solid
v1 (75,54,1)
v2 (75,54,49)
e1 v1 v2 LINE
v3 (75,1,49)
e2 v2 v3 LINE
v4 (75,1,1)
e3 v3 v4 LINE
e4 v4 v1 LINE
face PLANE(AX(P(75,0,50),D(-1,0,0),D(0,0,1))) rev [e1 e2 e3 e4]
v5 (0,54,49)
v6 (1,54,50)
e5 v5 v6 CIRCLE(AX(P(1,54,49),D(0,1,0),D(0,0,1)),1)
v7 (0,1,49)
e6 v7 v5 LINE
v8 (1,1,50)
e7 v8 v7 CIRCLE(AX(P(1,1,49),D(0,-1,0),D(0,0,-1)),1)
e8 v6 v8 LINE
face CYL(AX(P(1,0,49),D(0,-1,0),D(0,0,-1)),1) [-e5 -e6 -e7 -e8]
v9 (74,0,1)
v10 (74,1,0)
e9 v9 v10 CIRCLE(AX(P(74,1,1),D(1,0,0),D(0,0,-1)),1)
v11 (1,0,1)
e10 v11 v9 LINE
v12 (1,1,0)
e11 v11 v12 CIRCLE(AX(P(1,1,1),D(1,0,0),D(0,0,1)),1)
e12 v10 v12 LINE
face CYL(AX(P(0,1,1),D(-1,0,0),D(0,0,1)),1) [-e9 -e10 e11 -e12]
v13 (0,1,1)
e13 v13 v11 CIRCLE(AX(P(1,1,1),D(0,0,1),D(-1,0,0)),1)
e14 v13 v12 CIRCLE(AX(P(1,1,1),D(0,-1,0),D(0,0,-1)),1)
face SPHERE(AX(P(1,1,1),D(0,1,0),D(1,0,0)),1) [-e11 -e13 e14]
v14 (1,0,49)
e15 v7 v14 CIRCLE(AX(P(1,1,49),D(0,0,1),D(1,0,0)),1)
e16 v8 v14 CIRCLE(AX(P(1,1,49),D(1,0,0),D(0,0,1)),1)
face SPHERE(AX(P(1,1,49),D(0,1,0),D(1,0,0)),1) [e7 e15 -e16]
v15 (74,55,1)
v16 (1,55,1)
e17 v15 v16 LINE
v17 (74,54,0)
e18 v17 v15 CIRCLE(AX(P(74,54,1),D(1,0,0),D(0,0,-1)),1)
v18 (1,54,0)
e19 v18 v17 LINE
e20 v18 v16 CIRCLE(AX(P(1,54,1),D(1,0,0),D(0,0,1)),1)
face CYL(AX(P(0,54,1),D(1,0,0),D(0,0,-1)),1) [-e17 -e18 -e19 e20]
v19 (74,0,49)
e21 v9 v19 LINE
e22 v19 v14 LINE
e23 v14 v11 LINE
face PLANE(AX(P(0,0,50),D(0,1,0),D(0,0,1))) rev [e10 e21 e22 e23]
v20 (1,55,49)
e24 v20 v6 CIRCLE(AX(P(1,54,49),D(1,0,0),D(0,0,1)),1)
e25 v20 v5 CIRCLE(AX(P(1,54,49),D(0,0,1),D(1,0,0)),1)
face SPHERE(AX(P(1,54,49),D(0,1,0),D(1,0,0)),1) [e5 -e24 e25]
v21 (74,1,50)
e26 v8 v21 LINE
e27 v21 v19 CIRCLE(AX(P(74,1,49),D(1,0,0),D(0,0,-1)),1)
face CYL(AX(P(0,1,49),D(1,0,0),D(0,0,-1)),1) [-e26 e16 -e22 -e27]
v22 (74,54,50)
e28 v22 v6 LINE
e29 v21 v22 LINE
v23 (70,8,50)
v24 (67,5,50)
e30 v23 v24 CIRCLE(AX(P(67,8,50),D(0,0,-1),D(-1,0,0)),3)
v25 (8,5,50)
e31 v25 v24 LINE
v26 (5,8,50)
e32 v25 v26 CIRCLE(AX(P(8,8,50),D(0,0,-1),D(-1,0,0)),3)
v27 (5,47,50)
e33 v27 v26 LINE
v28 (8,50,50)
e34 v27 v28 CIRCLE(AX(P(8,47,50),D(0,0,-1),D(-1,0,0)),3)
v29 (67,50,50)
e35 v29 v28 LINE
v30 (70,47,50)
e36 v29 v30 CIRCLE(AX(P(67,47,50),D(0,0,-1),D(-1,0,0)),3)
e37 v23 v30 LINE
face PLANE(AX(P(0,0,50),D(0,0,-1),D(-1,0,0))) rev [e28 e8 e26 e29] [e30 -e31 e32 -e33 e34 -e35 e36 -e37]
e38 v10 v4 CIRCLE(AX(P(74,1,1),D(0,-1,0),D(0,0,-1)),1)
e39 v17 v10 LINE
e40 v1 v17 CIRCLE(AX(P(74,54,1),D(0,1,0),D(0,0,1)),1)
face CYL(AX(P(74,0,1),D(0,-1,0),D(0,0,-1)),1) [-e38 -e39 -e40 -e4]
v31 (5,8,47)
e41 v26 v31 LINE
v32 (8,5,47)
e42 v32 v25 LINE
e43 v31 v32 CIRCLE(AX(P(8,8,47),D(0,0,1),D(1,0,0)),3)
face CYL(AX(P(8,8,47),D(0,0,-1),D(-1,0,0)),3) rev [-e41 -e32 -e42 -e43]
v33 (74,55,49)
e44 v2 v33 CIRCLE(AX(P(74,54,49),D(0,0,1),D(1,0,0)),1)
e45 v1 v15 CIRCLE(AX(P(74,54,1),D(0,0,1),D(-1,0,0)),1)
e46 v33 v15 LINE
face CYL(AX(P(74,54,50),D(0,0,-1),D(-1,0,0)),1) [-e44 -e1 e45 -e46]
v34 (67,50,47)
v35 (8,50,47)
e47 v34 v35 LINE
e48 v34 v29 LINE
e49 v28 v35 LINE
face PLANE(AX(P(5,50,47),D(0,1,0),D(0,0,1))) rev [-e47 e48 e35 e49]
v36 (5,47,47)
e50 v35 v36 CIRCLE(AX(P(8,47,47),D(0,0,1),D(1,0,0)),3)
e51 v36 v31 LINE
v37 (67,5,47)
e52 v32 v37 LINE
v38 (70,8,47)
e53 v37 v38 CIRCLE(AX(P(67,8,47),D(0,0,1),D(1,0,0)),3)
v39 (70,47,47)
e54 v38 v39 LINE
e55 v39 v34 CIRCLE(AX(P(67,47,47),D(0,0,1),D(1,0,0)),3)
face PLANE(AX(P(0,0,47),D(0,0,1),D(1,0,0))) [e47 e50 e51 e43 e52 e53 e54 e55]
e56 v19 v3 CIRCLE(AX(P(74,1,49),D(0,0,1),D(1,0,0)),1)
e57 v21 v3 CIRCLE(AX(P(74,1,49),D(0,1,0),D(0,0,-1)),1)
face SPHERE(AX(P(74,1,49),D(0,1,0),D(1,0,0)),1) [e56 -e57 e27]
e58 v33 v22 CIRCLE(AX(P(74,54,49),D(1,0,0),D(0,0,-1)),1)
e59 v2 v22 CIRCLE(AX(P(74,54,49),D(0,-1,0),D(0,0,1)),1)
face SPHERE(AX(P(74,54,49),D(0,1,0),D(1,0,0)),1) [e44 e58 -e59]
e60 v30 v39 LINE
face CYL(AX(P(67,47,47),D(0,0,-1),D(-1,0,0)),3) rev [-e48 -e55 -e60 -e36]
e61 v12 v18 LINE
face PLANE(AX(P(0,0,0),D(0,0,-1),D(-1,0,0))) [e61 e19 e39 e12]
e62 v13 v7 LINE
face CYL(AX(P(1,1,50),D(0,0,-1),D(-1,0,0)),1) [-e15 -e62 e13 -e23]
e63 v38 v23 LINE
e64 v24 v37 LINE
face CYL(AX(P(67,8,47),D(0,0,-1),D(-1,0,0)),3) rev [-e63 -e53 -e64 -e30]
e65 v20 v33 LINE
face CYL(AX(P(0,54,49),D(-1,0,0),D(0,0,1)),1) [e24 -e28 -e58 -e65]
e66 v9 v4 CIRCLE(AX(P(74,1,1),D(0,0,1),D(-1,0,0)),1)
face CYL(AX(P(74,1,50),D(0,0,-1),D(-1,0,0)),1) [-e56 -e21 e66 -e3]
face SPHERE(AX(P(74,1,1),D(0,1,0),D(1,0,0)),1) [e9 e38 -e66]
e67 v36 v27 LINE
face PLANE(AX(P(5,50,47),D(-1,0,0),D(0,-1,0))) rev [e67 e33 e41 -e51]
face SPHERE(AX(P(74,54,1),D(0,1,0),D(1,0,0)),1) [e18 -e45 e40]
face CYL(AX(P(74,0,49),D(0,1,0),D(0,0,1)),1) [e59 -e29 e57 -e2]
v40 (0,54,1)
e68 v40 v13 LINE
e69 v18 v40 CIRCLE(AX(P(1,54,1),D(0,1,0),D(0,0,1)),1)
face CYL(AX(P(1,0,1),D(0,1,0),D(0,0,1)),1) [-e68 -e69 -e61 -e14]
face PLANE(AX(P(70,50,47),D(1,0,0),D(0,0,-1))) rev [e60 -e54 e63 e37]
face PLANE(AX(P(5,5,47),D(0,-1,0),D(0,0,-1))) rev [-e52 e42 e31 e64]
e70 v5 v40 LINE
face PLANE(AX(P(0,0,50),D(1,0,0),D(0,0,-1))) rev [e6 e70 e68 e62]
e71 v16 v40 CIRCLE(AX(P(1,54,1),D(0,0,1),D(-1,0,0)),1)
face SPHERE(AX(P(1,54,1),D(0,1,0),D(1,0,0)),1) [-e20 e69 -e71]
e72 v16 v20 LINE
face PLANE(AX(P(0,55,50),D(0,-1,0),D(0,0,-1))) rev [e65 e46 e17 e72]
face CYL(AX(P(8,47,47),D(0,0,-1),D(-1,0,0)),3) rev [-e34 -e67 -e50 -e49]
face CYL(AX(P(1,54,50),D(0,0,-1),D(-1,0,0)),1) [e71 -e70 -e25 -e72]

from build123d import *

# Parameters (mm, degrees)
SKETCH_1_W          = 75
SKETCH_1_H          = 55
EXTRUDE_1_DEPTH     = 50
SKETCH_2_W          = 65
SKETCH_2_H          = 45
CUT_EXTRUDE_1_DEPTH = 3
FILLET_1_R          = 3
FILLET_2_R          = 1


with BuildPart() as part:
    # 草图1 → 凸台-拉伸1 (new body)
    with BuildSketch(Plane.XY):
        with Locations((37.5, 27.5)):
            Rectangle(SKETCH_1_W, SKETCH_1_H)
    extrude(amount=EXTRUDE_1_DEPTH)

    # 草图2 → 切除-拉伸1 (cut)
    with BuildSketch(Plane.XY.offset(50)):
        with Locations((37.5, 27.5)):
            Rectangle(SKETCH_2_W, SKETCH_2_H)
    extrude(amount=-CUT_EXTRUDE_1_DEPTH, mode=Mode.SUBTRACT)

    # 圆角1
    fillet_1_edges = [part.edges().sort_by_distance(p)[0] for p in [
        (5, 5, 48.5),
        (5, 50, 48.5),
        (70, 50, 48.5),
        (70, 5, 48.5),
    ]]
    fillet(fillet_1_edges, radius=FILLET_1_R)

    # 圆角2
    fillet_2_edges = [part.edges().sort_by_distance(p)[0] for p in [
        (75, 27.5, 50),
        (37.5, 55, 50),
        (0, 27.5, 50),
        (37.5, 55, 0),
        (75, 27.5, 0),
        (37.5, 0, 0),
        (0, 27.5, 0),
        (0, 55, 25),
        (75, 55, 25),
        (75, 0, 25),
        (0, 0, 25),
        (37.5, 0, 50),
    ]]
    fillet(fillet_2_edges, radius=FILLET_2_R)


solid = part.part
